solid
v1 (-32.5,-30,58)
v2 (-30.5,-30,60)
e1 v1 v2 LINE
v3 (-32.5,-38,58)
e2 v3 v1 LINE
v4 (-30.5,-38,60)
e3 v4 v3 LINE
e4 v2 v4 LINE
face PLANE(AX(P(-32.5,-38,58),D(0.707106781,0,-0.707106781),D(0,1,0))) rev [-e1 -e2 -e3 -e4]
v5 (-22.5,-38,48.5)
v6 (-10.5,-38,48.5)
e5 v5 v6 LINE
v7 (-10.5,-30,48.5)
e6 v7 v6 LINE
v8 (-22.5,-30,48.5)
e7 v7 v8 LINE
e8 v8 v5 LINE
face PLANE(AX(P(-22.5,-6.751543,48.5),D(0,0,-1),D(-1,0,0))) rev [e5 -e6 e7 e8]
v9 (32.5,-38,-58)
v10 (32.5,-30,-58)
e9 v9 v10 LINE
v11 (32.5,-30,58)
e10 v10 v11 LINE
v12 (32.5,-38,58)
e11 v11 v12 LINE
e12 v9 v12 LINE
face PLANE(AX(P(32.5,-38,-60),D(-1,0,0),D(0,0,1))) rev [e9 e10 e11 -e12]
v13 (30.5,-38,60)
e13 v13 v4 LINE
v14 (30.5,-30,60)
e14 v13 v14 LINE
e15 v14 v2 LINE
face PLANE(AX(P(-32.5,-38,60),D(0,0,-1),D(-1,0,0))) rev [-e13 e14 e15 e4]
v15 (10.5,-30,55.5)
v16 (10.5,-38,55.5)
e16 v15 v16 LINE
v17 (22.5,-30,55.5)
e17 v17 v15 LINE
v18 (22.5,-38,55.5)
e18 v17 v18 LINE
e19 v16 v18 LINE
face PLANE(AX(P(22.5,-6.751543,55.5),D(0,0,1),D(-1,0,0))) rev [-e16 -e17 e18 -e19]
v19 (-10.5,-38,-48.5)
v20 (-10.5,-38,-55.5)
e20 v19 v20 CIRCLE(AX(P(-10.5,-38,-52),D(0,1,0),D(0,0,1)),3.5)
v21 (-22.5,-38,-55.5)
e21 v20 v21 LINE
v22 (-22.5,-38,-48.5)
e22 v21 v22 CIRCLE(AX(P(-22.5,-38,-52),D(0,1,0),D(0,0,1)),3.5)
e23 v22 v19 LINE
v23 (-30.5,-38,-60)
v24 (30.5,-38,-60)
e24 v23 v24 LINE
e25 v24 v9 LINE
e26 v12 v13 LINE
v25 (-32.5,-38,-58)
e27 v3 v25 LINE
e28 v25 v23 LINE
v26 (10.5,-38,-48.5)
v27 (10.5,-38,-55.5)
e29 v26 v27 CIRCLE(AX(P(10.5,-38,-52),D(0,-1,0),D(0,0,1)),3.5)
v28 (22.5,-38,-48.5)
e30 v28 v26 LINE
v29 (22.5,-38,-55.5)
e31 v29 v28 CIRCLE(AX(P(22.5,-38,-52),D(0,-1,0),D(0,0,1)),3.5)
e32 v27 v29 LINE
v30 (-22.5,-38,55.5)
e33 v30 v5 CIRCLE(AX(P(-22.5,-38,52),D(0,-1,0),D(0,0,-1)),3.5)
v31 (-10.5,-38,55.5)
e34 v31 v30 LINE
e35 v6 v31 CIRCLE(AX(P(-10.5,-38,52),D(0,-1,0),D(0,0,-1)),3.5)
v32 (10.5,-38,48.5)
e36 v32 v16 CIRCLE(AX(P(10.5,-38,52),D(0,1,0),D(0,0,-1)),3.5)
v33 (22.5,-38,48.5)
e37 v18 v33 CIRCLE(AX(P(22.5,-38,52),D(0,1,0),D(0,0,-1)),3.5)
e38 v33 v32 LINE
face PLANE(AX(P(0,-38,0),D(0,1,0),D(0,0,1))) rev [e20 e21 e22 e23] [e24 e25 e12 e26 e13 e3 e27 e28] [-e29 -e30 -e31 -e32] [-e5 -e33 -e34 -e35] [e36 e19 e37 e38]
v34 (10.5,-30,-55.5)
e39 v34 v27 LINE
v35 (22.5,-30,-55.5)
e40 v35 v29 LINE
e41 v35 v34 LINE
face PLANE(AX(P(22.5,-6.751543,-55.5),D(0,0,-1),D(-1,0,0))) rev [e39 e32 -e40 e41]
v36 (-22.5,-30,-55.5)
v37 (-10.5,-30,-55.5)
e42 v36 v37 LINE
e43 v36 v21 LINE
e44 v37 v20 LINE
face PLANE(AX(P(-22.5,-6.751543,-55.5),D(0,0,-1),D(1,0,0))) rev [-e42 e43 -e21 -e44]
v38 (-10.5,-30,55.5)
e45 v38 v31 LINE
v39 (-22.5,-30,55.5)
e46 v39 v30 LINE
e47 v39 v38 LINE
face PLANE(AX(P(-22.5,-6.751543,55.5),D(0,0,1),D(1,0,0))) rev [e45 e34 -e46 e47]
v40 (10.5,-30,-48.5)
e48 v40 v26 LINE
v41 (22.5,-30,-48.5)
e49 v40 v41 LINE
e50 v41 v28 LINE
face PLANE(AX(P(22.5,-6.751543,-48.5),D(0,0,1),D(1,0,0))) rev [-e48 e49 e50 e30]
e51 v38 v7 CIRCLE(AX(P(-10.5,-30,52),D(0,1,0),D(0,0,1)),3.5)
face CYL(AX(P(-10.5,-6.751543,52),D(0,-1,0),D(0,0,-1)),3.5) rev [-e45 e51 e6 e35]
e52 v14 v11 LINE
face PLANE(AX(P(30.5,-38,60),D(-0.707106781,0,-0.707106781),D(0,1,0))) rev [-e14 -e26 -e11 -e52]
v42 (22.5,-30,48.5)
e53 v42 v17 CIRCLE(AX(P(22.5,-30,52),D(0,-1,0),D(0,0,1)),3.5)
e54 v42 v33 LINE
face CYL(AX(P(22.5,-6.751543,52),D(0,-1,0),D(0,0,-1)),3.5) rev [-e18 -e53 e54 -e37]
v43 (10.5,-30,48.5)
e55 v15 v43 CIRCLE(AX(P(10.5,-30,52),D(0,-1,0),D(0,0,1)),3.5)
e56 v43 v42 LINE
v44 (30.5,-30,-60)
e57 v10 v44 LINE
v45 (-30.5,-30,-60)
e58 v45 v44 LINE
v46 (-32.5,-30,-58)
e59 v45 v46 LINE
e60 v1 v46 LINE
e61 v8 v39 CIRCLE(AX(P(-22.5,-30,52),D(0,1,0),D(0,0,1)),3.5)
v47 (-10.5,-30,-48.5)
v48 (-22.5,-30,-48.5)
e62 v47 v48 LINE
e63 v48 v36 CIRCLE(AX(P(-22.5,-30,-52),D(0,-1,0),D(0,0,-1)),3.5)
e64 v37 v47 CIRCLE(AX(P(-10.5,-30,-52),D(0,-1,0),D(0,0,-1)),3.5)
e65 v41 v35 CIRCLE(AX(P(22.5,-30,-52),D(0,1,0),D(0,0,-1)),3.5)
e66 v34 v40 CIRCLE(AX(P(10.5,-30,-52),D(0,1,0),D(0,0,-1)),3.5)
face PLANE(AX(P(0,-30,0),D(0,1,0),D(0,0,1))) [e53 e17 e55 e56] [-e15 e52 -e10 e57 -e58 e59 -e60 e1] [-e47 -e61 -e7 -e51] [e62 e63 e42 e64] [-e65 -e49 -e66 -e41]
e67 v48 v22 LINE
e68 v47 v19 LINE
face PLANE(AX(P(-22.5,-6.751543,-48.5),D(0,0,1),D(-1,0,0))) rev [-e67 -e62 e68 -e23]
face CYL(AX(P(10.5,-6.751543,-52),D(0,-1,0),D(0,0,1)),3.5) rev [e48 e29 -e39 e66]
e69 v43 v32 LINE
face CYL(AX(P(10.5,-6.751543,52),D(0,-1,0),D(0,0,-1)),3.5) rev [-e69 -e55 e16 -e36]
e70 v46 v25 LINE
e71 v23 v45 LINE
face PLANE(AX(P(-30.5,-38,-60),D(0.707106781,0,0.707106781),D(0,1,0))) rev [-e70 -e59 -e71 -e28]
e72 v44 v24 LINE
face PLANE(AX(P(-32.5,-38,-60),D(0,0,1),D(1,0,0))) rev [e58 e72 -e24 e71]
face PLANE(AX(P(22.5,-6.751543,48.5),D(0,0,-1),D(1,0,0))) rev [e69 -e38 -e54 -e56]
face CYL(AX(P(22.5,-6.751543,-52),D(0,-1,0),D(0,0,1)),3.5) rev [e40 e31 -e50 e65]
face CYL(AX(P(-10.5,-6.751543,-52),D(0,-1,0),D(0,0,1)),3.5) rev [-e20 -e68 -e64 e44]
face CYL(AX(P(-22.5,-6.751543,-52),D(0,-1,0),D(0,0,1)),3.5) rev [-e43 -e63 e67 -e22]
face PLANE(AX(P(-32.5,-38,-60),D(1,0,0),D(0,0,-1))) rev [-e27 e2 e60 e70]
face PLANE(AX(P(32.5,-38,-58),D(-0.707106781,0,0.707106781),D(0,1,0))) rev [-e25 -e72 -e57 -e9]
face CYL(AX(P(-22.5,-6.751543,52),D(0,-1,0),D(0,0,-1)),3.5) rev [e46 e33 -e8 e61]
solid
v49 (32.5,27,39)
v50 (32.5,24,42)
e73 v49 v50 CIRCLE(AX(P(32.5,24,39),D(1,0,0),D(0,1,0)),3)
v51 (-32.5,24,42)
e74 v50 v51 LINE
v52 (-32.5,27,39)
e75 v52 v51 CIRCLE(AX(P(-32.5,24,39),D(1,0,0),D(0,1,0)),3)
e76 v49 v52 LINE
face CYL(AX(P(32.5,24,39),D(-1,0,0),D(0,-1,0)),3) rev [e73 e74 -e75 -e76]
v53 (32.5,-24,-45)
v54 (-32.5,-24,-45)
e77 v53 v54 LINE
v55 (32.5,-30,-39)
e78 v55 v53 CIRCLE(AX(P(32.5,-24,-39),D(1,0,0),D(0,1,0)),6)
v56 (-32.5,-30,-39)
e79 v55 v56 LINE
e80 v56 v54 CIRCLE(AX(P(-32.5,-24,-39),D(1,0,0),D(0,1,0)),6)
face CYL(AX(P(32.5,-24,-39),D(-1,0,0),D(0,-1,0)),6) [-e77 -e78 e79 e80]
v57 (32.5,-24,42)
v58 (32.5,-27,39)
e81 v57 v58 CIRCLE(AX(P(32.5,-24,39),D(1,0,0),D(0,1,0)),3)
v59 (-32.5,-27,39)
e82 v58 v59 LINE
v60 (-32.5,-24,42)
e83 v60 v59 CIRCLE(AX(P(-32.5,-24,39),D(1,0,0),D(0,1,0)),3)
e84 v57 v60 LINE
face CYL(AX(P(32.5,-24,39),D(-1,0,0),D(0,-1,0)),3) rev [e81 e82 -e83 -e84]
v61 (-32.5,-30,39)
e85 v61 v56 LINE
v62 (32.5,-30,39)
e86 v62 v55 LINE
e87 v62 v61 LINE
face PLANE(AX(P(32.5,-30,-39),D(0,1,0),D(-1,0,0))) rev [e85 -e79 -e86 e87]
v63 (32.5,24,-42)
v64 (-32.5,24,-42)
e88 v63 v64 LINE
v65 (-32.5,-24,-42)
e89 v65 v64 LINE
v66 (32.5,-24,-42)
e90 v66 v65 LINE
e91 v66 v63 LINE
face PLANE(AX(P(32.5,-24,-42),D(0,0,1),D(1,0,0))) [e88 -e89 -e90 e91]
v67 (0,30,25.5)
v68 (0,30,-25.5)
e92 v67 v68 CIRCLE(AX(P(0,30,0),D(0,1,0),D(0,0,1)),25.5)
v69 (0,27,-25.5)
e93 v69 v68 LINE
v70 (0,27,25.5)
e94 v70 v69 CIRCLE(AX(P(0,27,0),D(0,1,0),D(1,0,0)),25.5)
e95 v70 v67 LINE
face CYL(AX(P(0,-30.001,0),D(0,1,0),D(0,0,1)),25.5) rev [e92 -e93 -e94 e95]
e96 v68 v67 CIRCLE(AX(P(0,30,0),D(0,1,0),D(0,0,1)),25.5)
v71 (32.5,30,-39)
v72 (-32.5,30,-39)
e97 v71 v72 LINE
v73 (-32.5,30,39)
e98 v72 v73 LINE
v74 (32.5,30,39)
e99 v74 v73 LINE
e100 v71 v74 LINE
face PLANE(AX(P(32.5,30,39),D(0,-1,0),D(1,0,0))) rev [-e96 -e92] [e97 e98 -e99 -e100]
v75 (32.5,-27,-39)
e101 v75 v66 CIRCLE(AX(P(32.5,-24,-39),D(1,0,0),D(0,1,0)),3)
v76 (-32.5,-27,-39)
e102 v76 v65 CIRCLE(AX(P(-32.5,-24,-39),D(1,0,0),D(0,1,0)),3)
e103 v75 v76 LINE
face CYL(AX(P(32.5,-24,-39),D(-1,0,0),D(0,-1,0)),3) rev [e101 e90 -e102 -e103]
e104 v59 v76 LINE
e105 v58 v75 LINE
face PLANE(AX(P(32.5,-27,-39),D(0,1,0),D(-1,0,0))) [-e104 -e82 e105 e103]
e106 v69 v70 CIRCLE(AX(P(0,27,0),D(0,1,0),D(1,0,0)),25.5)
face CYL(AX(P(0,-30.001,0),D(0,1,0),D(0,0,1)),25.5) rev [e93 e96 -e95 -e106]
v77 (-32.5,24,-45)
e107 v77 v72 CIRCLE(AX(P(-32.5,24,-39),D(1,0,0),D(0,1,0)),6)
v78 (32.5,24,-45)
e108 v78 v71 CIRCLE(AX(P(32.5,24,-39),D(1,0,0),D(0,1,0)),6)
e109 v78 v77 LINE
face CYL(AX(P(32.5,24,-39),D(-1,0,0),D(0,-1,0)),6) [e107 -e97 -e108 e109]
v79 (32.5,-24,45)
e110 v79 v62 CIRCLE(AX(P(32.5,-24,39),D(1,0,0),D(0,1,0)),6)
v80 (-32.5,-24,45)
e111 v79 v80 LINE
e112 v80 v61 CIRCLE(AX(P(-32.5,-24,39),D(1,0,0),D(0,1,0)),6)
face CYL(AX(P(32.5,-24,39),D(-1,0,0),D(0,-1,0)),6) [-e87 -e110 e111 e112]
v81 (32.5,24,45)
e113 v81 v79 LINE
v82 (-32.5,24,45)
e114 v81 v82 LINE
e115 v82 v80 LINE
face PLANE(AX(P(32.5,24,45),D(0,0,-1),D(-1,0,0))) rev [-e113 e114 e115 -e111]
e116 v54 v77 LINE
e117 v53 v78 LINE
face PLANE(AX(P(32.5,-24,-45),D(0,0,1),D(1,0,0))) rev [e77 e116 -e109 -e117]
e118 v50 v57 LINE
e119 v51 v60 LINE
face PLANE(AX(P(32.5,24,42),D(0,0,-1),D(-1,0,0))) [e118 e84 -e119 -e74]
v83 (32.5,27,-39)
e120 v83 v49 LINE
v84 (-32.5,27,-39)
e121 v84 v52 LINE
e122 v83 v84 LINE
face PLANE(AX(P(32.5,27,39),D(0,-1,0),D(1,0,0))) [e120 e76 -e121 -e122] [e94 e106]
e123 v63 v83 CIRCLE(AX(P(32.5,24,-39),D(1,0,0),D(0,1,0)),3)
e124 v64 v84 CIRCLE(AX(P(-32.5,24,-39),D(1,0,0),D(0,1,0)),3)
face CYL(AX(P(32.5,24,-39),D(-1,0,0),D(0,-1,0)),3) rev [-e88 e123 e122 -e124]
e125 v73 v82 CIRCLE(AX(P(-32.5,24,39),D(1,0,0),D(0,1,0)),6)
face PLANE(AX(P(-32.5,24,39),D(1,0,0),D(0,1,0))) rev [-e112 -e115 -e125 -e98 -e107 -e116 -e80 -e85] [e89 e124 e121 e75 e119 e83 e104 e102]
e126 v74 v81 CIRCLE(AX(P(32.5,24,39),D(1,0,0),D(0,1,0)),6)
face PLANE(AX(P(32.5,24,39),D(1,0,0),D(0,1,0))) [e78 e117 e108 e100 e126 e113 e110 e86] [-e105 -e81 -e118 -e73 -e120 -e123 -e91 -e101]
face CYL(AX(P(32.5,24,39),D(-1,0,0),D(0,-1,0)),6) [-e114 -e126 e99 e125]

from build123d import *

# Parameters (mm, degrees)
GB_T6728_2002_90_X_60_X_3_1_DEPTH = 65
CUT_EXTRUDE_1_REACH               = 83.739
SKETCH_4_R                        = 25.5
SKETCH_7_W                        = 65
SKETCH_7_H                        = 120
EXTRUDE_1_DEPTH                   = 8
CUT_EXTRUDE_5_DEPTH               = 11
MIRROR_3_COPY_1_DEPTH             = 11
CHAMFER_1_SIZE                    = 2


with BuildPart() as part:
    # Sketch11 → 冷弯空心矩管gb∕t6728-2002 90 X 60 X 3(1) (new body)
    with BuildSketch(Plane.YZ.offset(-32.5)):
        with BuildLine():
            Line((-24, -45), (24, -45))
            ThreePointArc((24, -45), (28.242640687, -43.242640687), (30, -39))
            Line((30, -39), (30, 39))
            ThreePointArc((30, 39), (28.242640687, 43.242640687), (24, 45))
            Line((24, 45), (-24, 45))
            ThreePointArc((-24, 45), (-28.242640687, 43.242640687), (-30, 39))
            Line((-30, 39), (-30, -39))
            ThreePointArc((-30, -39), (-28.242640687, -43.242640687), (-24, -45))
        make_face()
        with BuildLine():
            Line((-24, -42), (24, -42))
            ThreePointArc((24, -42), (26.121320344, -41.121320344), (27, -39))
            Line((27, -39), (27, 39))
            ThreePointArc((27, 39), (26.121320344, 41.121320344), (24, 42))
            Line((24, 42), (-24, 42))
            ThreePointArc((-24, 42), (-26.121320344, 41.121320344), (-27, 39))
            Line((-27, 39), (-27, -39))
            ThreePointArc((-27, -39), (-26.121320344, -41.121320344), (-24, -42))
        make_face(mode=Mode.SUBTRACT)
    extrude(amount=GB_T6728_2002_90_X_60_X_3_1_DEPTH)

    # 草图4 → 切除-拉伸1 (cut, up to next)
    with BuildSketch(Plane(origin=(0, 30, 0), x_dir=(1, 0, 0), z_dir=(0, 1, 0)), mode=Mode.PRIVATE) as cut_extrude_1_sk1:
        with Locations(Location((0, 0, 0), (0, 0, 270))):
            Circle(SKETCH_4_R)
    cut_extrude_1_tool1 = extrude(cut_extrude_1_sk1.sketch, amount=-CUT_EXTRUDE_1_REACH, mode=Mode.PRIVATE) & part.part
    add(cut_extrude_1_tool1.solids().sort_by_distance((0, 30, 0))[0], mode=Mode.SUBTRACT)


with BuildPart() as body_2:
    # 草图7 → 凸台-拉伸1 (new body)
    with BuildSketch(Plane.XZ.offset(30)):
        Rectangle(SKETCH_7_W, SKETCH_7_H)
    extrude(amount=EXTRUDE_1_DEPTH)

    # 草图8 → 切除-拉伸5 (cut)
    with BuildSketch(Plane.XZ.offset(38)):
        with BuildLine():
            Line((-22.5, 55.5), (-10.5, 55.5))
            ThreePointArc((-10.5, 55.5), (-7, 52), (-10.5, 48.5))
            Line((-10.5, 48.5), (-22.5, 48.5))
            ThreePointArc((-22.5, 48.5), (-26, 52), (-22.5, 55.5))
        make_face()
    cut_extrude_5 = extrude(amount=-CUT_EXTRUDE_5_DEPTH, mode=Mode.SUBTRACT)

    # 镜向2: 切除-拉伸5 across plane
    add(cut_extrude_5.mirror(Plane(origin=(0, 0, 0), x_dir=(0, 0, 1), z_dir=(1, 0, 0))), mode=Mode.SUBTRACT)

    # 镜向3: 切除-拉伸5 across plane
    add(cut_extrude_5.mirror(Plane.XY), mode=Mode.SUBTRACT)

    # 镜向3 copy 1 sketch → 镜向3 copy 1 (cut)
    with BuildSketch(Plane(origin=(0, -38, 0), x_dir=(-1, 0, 0), z_dir=(0, -1, 0))):
        with BuildLine():
            Line((-22.5, 55.5), (-10.5, 55.5))
            ThreePointArc((-10.5, 55.5), (-7, 52), (-10.5, 48.5))
            Line((-10.5, 48.5), (-22.5, 48.5))
            ThreePointArc((-22.5, 48.5), (-26, 52), (-22.5, 55.5))
        make_face()
    extrude(amount=-MIRROR_3_COPY_1_DEPTH, mode=Mode.SUBTRACT)

    # 倒角1
    chamfer_1_edges = [body_2.edges().sort_by_distance(p)[0] for p in [
        (32.5, -34, -60),
        (-32.5, -34, -60),
        (-32.5, -34, 60),
        (32.5, -34, 60),
    ]]
    chamfer(chamfer_1_edges, length=CHAMFER_1_SIZE)


solid = Compound([part.part, body_2.part])
